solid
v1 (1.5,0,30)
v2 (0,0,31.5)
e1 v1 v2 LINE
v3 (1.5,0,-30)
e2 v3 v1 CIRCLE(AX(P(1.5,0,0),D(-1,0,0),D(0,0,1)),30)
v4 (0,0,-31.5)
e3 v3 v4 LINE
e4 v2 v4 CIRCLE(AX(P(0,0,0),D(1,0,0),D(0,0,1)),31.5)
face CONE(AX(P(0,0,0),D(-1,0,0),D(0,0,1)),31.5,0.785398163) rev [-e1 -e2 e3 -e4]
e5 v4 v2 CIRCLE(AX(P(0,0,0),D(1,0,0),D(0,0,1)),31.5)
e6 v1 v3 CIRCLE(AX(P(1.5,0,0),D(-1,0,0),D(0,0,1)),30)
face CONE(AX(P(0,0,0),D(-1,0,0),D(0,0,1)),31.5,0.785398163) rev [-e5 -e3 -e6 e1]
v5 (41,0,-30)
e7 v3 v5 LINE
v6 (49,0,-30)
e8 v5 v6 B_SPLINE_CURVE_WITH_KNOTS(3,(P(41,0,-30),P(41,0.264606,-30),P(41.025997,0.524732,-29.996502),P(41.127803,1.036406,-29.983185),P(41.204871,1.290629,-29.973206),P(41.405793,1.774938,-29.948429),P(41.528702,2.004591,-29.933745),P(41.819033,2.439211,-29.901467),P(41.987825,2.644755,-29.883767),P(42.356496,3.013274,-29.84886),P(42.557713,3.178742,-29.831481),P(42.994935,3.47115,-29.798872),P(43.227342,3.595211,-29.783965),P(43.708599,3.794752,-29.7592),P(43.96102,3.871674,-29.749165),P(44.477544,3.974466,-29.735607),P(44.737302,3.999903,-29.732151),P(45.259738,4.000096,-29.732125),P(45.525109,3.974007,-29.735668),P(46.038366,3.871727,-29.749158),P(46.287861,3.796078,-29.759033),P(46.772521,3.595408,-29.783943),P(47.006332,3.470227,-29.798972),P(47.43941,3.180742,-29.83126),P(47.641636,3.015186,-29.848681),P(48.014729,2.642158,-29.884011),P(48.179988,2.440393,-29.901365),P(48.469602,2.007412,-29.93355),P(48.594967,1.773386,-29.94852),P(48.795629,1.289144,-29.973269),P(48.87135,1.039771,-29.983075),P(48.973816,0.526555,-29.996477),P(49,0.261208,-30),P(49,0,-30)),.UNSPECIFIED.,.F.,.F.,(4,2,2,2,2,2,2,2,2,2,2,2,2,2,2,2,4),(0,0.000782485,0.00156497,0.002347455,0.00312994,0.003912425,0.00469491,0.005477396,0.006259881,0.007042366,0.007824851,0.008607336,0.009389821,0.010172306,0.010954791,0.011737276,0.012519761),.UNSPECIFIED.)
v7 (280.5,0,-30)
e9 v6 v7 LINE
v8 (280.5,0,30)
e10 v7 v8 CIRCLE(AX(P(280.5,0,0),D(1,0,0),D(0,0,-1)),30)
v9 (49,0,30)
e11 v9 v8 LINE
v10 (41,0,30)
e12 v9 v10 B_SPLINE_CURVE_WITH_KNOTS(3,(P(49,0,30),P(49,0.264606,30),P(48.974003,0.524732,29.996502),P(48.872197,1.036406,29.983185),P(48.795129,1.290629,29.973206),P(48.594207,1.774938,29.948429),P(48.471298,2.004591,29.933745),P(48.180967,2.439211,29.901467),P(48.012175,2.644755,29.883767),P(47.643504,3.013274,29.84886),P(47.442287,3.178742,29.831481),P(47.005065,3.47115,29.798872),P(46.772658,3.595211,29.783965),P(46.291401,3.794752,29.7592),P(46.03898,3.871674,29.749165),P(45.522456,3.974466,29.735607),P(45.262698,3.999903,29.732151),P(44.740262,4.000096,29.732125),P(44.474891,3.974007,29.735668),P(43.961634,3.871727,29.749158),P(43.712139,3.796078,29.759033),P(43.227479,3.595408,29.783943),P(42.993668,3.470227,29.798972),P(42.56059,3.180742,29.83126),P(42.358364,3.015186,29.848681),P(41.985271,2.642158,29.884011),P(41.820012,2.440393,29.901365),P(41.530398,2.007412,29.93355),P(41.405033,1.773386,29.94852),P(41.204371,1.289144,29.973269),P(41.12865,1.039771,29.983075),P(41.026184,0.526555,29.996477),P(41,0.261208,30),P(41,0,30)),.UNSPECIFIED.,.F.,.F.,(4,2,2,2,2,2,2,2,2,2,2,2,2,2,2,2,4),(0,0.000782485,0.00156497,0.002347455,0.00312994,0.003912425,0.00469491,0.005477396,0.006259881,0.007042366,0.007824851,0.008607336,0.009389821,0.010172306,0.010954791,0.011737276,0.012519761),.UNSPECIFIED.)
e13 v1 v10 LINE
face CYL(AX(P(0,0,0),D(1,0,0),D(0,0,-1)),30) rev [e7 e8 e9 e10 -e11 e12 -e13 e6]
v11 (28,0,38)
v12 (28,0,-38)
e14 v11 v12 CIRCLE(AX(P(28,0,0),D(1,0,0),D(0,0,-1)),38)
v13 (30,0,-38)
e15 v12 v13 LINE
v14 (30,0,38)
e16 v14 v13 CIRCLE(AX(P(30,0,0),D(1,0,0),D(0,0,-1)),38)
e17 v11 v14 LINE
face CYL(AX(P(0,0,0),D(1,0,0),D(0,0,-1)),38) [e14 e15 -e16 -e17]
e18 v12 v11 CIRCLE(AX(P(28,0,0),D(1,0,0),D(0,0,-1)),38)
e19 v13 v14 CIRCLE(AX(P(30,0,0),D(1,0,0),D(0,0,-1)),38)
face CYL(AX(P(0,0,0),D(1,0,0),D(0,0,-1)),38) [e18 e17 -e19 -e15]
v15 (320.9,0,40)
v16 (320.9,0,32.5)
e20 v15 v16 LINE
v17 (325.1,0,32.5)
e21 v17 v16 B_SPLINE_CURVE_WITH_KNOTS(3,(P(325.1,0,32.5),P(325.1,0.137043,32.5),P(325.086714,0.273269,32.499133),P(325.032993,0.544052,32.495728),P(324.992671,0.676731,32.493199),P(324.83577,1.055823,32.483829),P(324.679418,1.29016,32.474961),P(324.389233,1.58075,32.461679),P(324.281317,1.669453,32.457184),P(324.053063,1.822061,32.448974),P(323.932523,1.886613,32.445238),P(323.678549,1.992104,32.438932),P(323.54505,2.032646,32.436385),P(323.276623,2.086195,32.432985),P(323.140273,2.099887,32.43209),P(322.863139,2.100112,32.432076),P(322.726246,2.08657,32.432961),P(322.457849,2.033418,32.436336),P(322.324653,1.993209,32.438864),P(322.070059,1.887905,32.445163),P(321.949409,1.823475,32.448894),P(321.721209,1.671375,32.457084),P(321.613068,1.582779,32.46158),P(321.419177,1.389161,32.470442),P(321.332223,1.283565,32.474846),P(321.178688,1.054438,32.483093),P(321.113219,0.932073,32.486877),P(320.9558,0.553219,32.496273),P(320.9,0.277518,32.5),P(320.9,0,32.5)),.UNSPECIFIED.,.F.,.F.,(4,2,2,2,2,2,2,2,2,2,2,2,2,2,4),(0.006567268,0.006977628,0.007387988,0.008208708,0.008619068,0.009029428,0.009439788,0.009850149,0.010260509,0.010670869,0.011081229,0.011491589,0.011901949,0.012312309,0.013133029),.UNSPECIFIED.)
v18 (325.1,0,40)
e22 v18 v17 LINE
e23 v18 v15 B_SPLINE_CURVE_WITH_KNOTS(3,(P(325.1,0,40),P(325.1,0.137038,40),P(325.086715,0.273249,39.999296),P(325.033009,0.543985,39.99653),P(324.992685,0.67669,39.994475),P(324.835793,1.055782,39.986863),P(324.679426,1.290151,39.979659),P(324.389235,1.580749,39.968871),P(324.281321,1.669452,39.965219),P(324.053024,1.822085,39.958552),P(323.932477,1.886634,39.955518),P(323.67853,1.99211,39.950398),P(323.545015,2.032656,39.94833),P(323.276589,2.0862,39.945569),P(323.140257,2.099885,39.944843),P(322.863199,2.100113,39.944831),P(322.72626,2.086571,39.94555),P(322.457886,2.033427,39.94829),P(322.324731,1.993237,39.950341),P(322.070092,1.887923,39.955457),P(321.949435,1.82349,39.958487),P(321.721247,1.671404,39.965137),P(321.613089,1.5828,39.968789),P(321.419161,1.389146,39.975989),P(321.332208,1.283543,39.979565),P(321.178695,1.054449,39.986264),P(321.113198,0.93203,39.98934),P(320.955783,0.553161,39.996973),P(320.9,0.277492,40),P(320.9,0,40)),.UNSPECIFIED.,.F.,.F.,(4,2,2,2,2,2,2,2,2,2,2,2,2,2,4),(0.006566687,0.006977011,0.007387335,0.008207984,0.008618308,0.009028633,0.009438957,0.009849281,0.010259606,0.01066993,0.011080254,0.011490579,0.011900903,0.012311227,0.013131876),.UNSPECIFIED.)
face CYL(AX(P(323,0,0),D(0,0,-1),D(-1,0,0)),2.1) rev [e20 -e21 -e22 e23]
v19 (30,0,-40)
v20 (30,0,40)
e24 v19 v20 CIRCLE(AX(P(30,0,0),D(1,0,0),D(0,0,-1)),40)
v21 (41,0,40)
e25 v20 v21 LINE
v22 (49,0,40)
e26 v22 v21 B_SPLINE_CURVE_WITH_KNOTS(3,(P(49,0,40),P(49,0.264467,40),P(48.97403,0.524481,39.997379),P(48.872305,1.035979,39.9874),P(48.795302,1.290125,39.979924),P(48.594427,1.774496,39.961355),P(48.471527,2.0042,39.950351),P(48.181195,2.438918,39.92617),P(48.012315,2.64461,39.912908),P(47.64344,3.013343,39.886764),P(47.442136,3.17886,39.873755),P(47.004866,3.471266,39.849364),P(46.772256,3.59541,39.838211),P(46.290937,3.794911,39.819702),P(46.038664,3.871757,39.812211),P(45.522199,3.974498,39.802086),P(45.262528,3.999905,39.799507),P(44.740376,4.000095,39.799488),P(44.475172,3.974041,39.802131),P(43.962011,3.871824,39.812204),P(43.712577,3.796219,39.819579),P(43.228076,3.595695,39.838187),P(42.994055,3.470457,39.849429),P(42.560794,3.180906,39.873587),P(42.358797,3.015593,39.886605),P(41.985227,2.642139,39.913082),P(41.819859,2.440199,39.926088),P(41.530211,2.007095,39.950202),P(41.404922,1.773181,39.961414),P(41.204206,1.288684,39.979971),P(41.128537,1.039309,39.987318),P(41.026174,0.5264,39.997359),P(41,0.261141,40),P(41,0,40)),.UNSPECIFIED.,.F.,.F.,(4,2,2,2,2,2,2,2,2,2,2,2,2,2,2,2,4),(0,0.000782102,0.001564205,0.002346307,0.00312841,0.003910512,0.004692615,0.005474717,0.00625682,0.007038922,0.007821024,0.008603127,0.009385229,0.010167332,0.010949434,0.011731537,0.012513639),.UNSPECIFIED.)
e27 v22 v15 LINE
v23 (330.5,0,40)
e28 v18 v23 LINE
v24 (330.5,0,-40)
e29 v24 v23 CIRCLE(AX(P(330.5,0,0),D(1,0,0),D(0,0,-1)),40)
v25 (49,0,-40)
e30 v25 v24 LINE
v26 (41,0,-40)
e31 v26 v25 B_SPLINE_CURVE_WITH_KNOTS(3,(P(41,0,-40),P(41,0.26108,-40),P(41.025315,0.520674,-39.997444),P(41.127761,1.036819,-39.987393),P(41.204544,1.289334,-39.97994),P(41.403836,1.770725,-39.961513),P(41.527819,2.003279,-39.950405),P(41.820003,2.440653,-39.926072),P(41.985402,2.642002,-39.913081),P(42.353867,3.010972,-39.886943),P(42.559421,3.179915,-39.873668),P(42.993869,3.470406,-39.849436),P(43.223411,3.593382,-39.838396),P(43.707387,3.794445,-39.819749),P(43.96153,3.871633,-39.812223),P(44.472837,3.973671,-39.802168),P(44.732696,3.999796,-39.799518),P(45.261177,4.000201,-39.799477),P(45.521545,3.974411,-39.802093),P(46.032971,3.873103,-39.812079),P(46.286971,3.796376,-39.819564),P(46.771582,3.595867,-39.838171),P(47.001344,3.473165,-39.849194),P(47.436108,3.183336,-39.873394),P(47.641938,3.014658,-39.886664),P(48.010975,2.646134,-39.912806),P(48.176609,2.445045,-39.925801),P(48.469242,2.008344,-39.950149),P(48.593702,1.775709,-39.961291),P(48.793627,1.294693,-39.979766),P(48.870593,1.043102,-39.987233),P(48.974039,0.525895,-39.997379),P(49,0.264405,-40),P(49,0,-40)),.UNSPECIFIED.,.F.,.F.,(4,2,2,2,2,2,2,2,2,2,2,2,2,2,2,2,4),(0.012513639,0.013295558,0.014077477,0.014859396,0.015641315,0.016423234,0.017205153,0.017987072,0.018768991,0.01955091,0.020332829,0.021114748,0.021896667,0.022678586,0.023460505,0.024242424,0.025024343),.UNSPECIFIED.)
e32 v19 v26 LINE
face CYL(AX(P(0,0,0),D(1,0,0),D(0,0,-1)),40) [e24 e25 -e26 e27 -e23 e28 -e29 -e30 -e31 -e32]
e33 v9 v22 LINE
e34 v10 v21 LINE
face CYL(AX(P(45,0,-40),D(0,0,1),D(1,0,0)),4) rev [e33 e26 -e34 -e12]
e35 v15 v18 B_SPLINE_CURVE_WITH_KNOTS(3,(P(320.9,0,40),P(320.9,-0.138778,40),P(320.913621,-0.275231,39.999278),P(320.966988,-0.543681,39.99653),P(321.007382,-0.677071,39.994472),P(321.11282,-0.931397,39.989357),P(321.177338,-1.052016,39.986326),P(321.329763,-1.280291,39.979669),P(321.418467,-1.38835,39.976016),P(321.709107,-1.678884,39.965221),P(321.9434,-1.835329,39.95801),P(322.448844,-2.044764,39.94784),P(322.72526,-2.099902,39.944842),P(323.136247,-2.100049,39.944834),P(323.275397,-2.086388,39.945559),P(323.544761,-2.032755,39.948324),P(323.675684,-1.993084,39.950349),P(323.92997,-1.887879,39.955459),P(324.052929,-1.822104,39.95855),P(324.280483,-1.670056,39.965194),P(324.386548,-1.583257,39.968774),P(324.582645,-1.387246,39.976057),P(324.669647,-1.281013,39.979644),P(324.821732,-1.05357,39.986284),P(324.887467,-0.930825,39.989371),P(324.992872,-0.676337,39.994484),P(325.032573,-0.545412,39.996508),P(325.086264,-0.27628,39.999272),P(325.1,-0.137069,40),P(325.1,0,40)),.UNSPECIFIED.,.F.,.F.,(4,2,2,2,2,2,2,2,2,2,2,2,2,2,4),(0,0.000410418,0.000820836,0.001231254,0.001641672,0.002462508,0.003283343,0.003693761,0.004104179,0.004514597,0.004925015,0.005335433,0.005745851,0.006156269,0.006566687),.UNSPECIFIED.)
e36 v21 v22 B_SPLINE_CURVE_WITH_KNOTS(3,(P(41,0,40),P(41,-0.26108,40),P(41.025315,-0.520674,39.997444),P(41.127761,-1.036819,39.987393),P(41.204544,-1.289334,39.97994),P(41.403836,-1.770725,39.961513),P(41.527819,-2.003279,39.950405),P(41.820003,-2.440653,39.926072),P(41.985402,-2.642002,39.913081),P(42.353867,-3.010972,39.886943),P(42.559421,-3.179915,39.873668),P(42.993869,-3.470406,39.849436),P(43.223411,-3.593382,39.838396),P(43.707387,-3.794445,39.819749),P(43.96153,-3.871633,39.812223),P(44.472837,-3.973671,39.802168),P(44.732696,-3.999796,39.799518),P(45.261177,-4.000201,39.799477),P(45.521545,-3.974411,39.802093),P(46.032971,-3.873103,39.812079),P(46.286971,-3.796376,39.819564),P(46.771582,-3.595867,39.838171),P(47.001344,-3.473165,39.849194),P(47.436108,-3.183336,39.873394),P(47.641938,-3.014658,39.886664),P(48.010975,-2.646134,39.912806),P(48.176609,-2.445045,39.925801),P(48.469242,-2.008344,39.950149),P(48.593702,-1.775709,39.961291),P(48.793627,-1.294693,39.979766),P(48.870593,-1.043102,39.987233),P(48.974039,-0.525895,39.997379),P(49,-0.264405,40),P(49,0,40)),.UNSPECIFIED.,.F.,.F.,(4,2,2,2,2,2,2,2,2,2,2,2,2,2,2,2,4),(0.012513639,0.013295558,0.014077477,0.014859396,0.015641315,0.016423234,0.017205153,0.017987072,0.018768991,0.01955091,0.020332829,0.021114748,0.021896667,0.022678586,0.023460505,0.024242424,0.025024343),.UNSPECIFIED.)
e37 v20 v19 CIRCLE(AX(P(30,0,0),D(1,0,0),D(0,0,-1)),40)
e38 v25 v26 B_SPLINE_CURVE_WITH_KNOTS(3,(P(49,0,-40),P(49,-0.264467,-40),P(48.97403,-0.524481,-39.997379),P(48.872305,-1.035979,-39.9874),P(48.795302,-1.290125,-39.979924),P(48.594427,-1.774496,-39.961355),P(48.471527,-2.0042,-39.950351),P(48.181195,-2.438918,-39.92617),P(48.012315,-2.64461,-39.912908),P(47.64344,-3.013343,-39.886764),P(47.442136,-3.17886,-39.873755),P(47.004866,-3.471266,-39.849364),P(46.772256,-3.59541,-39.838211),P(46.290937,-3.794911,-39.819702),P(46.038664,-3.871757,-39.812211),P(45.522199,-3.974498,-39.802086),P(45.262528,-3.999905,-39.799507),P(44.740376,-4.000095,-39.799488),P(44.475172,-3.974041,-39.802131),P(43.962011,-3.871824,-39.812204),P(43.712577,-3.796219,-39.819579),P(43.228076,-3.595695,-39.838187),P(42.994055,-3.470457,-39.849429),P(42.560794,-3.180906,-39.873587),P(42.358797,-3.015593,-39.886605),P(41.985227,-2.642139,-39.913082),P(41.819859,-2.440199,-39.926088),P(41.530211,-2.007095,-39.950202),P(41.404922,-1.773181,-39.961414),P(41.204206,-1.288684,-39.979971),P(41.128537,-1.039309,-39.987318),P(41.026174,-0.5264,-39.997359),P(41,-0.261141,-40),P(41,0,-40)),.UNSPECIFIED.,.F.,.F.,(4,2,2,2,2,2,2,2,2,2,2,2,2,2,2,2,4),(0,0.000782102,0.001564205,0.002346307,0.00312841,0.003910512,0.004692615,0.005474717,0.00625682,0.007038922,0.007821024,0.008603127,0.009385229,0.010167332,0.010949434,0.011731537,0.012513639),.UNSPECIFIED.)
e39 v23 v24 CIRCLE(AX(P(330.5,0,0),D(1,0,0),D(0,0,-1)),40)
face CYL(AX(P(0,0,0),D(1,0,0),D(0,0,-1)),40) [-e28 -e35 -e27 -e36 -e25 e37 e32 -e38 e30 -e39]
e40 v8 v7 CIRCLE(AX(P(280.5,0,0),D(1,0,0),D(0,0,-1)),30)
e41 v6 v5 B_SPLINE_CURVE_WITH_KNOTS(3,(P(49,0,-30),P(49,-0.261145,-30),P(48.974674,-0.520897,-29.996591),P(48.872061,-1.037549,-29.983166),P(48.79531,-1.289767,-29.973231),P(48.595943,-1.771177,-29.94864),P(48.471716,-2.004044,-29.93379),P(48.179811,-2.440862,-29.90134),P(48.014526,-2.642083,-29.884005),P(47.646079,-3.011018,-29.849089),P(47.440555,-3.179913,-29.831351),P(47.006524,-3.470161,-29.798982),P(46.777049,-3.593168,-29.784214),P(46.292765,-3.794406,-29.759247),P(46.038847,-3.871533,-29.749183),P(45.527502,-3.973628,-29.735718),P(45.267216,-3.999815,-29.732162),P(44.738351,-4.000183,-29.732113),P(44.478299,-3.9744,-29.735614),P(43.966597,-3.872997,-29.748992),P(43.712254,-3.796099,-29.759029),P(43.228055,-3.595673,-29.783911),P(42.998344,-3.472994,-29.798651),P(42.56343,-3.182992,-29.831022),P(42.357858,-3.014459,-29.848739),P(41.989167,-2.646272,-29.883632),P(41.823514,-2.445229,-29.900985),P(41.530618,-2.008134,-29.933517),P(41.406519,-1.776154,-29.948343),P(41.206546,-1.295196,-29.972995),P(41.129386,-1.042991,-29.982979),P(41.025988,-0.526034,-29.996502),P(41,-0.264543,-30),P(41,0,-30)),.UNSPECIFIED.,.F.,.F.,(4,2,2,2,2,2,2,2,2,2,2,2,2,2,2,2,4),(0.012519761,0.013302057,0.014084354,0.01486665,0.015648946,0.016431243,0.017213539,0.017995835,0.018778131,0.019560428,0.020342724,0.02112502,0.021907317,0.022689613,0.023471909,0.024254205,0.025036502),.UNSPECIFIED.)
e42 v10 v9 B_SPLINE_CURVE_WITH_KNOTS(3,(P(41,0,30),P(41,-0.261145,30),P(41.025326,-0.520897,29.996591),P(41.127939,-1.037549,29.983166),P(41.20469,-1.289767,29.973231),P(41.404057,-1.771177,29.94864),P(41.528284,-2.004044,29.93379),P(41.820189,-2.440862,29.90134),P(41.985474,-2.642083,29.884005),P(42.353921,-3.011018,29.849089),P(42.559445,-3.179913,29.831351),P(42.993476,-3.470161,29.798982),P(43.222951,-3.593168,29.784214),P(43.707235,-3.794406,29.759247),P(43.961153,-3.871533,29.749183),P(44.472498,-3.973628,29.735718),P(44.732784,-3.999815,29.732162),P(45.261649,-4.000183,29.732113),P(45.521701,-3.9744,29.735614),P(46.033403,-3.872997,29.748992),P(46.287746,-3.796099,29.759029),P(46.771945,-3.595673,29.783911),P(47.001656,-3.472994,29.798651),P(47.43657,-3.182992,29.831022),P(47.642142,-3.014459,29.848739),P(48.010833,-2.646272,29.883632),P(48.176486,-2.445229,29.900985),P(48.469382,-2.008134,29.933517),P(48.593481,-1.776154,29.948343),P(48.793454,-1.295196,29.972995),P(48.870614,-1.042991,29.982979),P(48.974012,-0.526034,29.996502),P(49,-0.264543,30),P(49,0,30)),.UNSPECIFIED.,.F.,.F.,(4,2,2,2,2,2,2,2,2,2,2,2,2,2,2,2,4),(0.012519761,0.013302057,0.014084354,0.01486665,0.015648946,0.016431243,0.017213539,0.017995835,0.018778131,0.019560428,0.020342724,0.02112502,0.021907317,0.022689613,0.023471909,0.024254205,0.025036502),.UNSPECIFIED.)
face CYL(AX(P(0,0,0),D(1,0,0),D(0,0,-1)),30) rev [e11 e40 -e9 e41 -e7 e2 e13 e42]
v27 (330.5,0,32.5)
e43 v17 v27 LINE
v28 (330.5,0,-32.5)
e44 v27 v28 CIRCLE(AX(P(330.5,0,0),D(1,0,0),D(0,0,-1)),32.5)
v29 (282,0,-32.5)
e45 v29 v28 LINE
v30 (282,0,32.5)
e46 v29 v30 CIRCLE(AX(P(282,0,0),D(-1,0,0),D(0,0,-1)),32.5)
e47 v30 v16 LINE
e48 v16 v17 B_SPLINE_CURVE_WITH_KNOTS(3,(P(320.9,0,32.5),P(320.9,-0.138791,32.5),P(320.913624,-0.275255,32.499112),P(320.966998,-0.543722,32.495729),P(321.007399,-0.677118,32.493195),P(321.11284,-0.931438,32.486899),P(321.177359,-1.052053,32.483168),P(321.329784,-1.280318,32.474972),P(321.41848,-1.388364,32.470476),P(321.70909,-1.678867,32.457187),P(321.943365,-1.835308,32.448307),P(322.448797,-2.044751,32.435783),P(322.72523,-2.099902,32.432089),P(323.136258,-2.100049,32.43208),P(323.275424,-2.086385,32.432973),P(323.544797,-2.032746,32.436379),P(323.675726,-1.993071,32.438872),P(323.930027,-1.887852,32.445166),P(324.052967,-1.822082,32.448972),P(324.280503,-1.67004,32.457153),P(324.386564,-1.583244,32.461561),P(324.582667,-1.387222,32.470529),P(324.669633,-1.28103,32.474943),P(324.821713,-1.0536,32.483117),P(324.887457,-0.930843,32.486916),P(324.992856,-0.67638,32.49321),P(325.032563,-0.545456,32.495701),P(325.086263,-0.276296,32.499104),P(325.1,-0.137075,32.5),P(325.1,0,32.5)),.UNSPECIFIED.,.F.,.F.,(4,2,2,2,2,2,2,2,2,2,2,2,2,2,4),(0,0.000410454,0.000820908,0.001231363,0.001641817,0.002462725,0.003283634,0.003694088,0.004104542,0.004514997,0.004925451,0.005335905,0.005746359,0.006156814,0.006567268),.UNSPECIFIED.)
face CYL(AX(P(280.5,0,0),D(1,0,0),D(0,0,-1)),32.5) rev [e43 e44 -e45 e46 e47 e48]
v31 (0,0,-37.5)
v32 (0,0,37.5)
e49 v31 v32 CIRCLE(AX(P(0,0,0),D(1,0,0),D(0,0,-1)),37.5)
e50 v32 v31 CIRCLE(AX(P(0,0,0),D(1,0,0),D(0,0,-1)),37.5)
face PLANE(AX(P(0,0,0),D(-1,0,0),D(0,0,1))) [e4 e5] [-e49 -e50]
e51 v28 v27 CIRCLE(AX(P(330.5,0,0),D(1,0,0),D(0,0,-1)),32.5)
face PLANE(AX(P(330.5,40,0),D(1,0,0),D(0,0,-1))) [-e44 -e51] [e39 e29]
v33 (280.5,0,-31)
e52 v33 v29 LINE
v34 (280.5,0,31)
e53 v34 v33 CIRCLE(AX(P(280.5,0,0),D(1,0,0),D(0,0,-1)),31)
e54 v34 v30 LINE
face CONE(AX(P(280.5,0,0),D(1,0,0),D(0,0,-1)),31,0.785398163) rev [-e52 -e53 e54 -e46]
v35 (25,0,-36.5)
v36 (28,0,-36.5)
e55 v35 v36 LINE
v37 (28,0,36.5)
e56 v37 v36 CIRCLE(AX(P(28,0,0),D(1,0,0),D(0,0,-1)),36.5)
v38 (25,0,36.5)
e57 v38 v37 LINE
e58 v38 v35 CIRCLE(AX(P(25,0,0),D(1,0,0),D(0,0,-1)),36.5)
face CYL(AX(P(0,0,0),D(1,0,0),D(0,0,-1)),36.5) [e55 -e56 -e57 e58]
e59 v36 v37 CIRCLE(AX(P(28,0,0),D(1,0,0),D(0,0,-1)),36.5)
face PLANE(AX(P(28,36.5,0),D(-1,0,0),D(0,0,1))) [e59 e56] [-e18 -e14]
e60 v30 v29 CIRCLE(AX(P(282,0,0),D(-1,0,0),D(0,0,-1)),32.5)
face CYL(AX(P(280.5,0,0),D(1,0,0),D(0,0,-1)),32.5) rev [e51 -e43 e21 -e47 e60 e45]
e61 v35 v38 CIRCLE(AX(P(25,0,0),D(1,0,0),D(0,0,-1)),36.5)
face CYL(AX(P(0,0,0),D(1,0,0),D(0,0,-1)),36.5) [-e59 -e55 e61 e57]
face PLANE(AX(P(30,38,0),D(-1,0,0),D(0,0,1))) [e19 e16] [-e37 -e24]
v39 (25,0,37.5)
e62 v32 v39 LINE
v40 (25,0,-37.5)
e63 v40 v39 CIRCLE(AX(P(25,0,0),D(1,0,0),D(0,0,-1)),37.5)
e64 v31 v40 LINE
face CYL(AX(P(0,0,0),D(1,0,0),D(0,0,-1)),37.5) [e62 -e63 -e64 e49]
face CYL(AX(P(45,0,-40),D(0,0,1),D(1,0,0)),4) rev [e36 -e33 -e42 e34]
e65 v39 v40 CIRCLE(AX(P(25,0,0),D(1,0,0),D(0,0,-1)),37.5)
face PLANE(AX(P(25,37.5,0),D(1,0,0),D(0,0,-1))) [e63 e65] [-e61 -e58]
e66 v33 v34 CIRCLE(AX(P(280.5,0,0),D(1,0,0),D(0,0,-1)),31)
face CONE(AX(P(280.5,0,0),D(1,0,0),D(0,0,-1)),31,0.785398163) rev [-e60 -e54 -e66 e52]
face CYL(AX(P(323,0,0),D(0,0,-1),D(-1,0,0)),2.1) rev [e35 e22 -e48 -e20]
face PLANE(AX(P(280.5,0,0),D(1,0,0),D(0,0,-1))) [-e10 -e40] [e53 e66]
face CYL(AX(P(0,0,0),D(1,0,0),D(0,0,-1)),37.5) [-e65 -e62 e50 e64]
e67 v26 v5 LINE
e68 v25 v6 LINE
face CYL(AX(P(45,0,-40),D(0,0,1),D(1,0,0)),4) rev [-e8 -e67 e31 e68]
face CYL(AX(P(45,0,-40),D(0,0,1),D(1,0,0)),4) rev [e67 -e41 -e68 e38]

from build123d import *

# Parameters (mm, degrees)
SKETCH2_R               = 32.5
CUT_EXTRUDE1_DEPTH      = 50
SKETCH3_R               = 30
CUT_EXTRUDE2_DEPTH      = 287.147252302
CHAMFER1_SIZE           = 1.5
CHAMFER2_SIZE           = 1.5
CUT_EXTRUDE3_DEPTH      = 336.306203343
CUT_EXTRUDE3_DEPTH_BACK = 336.306203343
SKETCH4_R               = 4
SKETCH7_W               = 2.1
SKETCH7_H               = 40


with BuildPart() as part:
    # Sketch1 → Revolve1 (revolve)
    with BuildSketch(Plane.XY, mode=Mode.PRIVATE) as revolve1_sk:
        Polygon((0, 0), (0, 37.5), (25, 37.5), (25, 36.5), (28, 36.5), (28, 38), (30, 38), (30, 40), (330.5, 40), (330.5, 0), align=None)
    revolve(revolve1_sk.sketch.rotate(Axis((0, 0, 0), (-1, 0, 0)), 90), axis=Axis((0, 0, 0), (-1, 0, 0)))

    # Sketch2 → Cut-Extrude1 (cut)
    with BuildSketch(Plane(origin=(330.5, 0, 0), x_dir=(0, 0, -1), z_dir=(1, 0, 0))):
        Circle(SKETCH2_R)
    extrude(amount=-CUT_EXTRUDE1_DEPTH, mode=Mode.SUBTRACT)

    # Sketch3 → Cut-Extrude2 (cut, through all)
    with BuildSketch(Plane(origin=(280.5, 0, 0), x_dir=(0, 0, -1), z_dir=(1, 0, 0))):
        Circle(SKETCH3_R)
    extrude(amount=-CUT_EXTRUDE2_DEPTH, mode=Mode.SUBTRACT)

    # Chamfer1
    chamfer1_edges = [part.edges().sort_by_distance(p)[0] for p in [
        (280.5, 0, 32.5),
    ]]
    chamfer(chamfer1_edges, length=CHAMFER1_SIZE)

    # Chamfer2
    chamfer2_edges = [part.edges().sort_by_distance(p)[0] for p in [
        (0, 0, 30),
    ]]
    chamfer(chamfer2_edges, length=CHAMFER2_SIZE)

    # Sketch4 → Cut-Extrude3 (cut, two sides: drawn at the far end of the back side and taken through both)
    with BuildSketch(Plane.XY.offset(-CUT_EXTRUDE3_DEPTH_BACK)):
        with Locations((45, 0)):
            Circle(SKETCH4_R)
    extrude(amount=CUT_EXTRUDE3_DEPTH + CUT_EXTRUDE3_DEPTH_BACK, mode=Mode.SUBTRACT)

    # Sketch7 → M5 Tapped Hole2 (revolve, cut)
    with BuildSketch(Plane.YZ.offset(323)):
        with Locations((1.05, 20)):
            Rectangle(SKETCH7_W, SKETCH7_H)
    revolve(axis=Axis((323, 0, -6.35), (0, 0, 1)), mode=Mode.SUBTRACT)


solid = part.part
